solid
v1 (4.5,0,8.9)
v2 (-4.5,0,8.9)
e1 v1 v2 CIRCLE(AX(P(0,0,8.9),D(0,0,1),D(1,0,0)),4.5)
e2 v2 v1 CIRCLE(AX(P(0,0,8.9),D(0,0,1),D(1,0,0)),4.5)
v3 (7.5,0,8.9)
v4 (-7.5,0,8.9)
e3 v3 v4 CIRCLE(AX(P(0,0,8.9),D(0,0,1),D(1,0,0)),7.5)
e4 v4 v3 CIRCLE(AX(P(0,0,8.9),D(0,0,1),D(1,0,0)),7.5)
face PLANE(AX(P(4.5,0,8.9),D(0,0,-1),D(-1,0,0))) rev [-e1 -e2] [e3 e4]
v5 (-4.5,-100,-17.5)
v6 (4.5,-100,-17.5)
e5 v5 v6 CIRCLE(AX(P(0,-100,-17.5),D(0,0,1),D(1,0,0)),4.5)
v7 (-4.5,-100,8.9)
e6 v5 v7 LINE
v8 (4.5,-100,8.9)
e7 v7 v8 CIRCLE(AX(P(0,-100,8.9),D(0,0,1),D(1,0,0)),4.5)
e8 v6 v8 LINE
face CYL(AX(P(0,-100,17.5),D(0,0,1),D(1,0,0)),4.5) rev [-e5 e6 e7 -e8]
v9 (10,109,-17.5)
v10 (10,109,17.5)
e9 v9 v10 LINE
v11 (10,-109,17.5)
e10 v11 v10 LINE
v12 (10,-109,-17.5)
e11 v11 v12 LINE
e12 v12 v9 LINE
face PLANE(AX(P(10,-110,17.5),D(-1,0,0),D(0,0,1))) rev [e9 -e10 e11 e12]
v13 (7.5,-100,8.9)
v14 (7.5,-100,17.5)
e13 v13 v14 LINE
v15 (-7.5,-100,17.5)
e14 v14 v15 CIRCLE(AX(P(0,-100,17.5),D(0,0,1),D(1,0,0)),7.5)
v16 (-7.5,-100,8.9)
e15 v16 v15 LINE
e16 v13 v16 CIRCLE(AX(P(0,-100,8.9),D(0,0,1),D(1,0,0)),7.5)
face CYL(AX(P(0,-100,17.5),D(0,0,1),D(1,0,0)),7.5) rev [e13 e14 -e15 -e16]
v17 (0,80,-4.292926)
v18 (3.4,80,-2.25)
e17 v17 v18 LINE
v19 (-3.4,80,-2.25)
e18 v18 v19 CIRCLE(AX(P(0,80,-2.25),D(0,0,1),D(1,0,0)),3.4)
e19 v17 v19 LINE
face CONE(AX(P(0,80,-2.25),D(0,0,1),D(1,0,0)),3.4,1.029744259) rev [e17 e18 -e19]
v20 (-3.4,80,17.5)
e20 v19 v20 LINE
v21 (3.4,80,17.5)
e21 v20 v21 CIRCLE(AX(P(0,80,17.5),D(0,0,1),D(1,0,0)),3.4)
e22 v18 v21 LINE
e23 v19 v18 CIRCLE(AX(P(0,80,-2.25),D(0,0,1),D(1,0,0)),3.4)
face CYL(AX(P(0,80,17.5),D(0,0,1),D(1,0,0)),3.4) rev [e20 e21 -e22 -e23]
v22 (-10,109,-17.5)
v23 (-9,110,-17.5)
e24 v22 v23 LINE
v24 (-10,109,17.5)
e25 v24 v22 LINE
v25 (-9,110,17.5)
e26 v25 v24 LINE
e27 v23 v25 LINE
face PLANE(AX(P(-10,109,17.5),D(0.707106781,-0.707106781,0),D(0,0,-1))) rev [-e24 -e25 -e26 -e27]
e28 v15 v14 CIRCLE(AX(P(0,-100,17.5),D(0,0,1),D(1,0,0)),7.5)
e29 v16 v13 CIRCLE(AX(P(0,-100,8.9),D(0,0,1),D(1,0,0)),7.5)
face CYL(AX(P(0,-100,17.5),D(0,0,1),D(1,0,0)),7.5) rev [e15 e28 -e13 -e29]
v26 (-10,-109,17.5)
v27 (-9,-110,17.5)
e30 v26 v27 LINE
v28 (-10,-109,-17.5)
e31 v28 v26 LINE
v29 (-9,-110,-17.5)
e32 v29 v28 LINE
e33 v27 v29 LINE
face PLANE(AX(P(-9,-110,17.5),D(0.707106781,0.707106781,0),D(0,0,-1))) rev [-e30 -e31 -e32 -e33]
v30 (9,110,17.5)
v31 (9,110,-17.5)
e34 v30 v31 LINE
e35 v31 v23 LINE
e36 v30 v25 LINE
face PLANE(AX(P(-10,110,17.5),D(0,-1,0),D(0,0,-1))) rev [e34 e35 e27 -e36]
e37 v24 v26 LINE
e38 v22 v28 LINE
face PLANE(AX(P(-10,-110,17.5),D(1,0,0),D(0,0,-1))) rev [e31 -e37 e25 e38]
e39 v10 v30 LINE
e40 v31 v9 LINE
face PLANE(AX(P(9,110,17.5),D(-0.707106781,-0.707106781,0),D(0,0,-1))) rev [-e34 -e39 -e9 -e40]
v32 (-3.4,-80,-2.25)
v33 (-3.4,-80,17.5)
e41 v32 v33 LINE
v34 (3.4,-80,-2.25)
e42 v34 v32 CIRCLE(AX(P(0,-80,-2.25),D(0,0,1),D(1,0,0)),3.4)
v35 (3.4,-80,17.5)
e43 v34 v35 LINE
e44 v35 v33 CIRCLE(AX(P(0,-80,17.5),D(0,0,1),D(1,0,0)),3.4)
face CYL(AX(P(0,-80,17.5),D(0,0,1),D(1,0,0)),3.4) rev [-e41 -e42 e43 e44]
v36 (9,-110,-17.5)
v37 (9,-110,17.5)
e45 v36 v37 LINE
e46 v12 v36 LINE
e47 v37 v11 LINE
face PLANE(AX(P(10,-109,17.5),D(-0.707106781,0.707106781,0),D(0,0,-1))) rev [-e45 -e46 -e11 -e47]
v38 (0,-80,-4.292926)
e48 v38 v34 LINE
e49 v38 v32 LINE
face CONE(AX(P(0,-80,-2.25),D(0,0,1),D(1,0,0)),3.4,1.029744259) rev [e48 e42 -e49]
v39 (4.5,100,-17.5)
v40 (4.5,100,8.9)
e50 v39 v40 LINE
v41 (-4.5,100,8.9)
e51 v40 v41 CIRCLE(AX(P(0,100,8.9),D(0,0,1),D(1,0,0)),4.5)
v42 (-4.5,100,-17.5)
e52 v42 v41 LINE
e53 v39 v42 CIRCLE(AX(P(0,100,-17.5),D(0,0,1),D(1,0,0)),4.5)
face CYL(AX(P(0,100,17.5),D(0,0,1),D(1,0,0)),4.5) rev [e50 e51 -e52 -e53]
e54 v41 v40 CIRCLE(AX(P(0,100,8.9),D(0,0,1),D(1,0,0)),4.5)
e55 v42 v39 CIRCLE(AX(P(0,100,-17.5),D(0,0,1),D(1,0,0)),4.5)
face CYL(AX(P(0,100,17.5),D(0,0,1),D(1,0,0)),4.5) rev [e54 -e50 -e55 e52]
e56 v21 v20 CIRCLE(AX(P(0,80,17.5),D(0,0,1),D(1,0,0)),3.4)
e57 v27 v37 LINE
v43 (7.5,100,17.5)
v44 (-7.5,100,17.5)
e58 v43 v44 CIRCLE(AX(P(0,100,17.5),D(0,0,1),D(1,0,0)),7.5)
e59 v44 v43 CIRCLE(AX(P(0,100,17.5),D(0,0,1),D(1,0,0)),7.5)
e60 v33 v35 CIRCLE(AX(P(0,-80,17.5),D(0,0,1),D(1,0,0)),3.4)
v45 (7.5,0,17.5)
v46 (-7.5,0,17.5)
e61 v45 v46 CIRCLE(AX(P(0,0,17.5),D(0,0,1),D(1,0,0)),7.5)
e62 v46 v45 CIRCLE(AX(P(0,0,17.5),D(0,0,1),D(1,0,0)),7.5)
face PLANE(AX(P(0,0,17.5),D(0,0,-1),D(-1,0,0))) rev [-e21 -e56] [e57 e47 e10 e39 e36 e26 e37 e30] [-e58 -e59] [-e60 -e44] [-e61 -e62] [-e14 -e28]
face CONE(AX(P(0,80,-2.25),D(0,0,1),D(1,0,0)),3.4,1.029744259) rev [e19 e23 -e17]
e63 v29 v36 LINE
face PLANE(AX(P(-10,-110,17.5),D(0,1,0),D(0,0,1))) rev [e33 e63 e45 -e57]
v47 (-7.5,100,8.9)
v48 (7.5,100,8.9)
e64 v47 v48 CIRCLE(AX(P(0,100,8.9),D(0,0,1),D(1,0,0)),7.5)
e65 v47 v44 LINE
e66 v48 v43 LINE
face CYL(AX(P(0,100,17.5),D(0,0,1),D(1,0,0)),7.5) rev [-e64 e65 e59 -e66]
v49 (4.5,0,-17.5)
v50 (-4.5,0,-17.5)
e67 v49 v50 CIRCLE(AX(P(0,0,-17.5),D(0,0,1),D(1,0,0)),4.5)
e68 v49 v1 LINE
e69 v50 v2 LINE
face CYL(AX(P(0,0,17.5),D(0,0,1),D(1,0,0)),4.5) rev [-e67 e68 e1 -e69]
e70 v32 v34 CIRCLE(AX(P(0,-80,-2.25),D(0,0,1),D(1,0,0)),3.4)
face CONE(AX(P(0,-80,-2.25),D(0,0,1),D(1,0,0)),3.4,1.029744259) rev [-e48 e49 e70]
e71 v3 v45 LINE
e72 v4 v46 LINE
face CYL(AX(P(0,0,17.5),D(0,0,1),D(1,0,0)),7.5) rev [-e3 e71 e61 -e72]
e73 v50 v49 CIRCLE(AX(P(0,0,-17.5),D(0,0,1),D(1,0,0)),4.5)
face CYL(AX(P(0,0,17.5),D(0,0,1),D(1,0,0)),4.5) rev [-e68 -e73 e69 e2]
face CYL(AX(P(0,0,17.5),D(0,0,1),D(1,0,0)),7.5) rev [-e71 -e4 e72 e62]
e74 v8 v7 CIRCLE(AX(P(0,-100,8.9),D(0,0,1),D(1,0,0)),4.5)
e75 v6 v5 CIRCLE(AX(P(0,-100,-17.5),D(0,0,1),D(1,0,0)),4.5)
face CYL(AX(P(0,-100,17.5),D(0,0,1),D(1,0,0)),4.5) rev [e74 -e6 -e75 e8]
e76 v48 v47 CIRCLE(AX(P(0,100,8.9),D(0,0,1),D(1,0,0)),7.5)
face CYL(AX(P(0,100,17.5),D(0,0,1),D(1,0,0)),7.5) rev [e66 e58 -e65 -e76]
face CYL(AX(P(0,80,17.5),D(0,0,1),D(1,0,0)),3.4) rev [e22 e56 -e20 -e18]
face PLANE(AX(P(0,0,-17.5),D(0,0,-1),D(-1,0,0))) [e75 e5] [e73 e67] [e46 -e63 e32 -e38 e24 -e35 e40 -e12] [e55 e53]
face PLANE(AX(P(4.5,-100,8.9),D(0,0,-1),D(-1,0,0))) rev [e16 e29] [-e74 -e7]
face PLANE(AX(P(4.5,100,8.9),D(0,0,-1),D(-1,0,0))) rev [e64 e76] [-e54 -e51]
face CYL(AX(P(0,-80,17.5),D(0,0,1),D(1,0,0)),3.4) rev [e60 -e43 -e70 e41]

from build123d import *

# Parameters (mm, degrees)
SKETCH_1_W                   = 20
SKETCH_1_H                   = 220
EXTRUDE_1_DEPTH              = 17.5
HOLE_WIZARD_M8_1_D           = 9
HOLE_WIZARD_M8_1_CBORE_D     = 15
HOLE_WIZARD_M8_1_CBORE_DEPTH = 8.6
HOLE_WIZARD_M8_1_2_D         = 6.8
HOLE_WIZARD_M8_1_2_DEPTH     = 19.75
HOLE_WIZARD_M8_1_2_TIP       = 2.042926105
CHAMFER_1_SIZE               = 1


with BuildPart() as part:
    # 草图1 → 凸台-拉伸1 (new, symmetric)
    with BuildSketch(Plane.XY):
        Rectangle(SKETCH_1_W, SKETCH_1_H)
    extrude(amount=EXTRUDE_1_DEPTH, both=True)

    # Hole Wizard M8 _1 (through all)
    with Locations(Plane.XY.offset(17.5)):
        with Locations((0, 100), (0, 0), (0, -100)):
            CounterBoreHole(HOLE_WIZARD_M8_1_D / 2, HOLE_WIZARD_M8_1_CBORE_D / 2, HOLE_WIZARD_M8_1_CBORE_DEPTH)

    # Hole Wizard M8 _1 2
    with Locations(Plane.XY.offset(17.5)):
        with Locations((0, 80), (0, -80)):
            Hole(HOLE_WIZARD_M8_1_2_D / 2, depth=HOLE_WIZARD_M8_1_2_DEPTH)
            with Locations((0, 0, -(HOLE_WIZARD_M8_1_2_DEPTH + HOLE_WIZARD_M8_1_2_TIP / 2))):  # 118° drill point
                Cone(0, HOLE_WIZARD_M8_1_2_D / 2, HOLE_WIZARD_M8_1_2_TIP, mode=Mode.SUBTRACT)

    # 倒角1
    chamfer_1_edges = [part.edges().sort_by_distance(p)[0] for p in [
        (10, -110, 0),
        (-10, -110, 0),
        (-10, 110, 0),
        (10, 110, 0),
    ]]
    chamfer(chamfer_1_edges, length=CHAMFER_1_SIZE)


solid = part.part
